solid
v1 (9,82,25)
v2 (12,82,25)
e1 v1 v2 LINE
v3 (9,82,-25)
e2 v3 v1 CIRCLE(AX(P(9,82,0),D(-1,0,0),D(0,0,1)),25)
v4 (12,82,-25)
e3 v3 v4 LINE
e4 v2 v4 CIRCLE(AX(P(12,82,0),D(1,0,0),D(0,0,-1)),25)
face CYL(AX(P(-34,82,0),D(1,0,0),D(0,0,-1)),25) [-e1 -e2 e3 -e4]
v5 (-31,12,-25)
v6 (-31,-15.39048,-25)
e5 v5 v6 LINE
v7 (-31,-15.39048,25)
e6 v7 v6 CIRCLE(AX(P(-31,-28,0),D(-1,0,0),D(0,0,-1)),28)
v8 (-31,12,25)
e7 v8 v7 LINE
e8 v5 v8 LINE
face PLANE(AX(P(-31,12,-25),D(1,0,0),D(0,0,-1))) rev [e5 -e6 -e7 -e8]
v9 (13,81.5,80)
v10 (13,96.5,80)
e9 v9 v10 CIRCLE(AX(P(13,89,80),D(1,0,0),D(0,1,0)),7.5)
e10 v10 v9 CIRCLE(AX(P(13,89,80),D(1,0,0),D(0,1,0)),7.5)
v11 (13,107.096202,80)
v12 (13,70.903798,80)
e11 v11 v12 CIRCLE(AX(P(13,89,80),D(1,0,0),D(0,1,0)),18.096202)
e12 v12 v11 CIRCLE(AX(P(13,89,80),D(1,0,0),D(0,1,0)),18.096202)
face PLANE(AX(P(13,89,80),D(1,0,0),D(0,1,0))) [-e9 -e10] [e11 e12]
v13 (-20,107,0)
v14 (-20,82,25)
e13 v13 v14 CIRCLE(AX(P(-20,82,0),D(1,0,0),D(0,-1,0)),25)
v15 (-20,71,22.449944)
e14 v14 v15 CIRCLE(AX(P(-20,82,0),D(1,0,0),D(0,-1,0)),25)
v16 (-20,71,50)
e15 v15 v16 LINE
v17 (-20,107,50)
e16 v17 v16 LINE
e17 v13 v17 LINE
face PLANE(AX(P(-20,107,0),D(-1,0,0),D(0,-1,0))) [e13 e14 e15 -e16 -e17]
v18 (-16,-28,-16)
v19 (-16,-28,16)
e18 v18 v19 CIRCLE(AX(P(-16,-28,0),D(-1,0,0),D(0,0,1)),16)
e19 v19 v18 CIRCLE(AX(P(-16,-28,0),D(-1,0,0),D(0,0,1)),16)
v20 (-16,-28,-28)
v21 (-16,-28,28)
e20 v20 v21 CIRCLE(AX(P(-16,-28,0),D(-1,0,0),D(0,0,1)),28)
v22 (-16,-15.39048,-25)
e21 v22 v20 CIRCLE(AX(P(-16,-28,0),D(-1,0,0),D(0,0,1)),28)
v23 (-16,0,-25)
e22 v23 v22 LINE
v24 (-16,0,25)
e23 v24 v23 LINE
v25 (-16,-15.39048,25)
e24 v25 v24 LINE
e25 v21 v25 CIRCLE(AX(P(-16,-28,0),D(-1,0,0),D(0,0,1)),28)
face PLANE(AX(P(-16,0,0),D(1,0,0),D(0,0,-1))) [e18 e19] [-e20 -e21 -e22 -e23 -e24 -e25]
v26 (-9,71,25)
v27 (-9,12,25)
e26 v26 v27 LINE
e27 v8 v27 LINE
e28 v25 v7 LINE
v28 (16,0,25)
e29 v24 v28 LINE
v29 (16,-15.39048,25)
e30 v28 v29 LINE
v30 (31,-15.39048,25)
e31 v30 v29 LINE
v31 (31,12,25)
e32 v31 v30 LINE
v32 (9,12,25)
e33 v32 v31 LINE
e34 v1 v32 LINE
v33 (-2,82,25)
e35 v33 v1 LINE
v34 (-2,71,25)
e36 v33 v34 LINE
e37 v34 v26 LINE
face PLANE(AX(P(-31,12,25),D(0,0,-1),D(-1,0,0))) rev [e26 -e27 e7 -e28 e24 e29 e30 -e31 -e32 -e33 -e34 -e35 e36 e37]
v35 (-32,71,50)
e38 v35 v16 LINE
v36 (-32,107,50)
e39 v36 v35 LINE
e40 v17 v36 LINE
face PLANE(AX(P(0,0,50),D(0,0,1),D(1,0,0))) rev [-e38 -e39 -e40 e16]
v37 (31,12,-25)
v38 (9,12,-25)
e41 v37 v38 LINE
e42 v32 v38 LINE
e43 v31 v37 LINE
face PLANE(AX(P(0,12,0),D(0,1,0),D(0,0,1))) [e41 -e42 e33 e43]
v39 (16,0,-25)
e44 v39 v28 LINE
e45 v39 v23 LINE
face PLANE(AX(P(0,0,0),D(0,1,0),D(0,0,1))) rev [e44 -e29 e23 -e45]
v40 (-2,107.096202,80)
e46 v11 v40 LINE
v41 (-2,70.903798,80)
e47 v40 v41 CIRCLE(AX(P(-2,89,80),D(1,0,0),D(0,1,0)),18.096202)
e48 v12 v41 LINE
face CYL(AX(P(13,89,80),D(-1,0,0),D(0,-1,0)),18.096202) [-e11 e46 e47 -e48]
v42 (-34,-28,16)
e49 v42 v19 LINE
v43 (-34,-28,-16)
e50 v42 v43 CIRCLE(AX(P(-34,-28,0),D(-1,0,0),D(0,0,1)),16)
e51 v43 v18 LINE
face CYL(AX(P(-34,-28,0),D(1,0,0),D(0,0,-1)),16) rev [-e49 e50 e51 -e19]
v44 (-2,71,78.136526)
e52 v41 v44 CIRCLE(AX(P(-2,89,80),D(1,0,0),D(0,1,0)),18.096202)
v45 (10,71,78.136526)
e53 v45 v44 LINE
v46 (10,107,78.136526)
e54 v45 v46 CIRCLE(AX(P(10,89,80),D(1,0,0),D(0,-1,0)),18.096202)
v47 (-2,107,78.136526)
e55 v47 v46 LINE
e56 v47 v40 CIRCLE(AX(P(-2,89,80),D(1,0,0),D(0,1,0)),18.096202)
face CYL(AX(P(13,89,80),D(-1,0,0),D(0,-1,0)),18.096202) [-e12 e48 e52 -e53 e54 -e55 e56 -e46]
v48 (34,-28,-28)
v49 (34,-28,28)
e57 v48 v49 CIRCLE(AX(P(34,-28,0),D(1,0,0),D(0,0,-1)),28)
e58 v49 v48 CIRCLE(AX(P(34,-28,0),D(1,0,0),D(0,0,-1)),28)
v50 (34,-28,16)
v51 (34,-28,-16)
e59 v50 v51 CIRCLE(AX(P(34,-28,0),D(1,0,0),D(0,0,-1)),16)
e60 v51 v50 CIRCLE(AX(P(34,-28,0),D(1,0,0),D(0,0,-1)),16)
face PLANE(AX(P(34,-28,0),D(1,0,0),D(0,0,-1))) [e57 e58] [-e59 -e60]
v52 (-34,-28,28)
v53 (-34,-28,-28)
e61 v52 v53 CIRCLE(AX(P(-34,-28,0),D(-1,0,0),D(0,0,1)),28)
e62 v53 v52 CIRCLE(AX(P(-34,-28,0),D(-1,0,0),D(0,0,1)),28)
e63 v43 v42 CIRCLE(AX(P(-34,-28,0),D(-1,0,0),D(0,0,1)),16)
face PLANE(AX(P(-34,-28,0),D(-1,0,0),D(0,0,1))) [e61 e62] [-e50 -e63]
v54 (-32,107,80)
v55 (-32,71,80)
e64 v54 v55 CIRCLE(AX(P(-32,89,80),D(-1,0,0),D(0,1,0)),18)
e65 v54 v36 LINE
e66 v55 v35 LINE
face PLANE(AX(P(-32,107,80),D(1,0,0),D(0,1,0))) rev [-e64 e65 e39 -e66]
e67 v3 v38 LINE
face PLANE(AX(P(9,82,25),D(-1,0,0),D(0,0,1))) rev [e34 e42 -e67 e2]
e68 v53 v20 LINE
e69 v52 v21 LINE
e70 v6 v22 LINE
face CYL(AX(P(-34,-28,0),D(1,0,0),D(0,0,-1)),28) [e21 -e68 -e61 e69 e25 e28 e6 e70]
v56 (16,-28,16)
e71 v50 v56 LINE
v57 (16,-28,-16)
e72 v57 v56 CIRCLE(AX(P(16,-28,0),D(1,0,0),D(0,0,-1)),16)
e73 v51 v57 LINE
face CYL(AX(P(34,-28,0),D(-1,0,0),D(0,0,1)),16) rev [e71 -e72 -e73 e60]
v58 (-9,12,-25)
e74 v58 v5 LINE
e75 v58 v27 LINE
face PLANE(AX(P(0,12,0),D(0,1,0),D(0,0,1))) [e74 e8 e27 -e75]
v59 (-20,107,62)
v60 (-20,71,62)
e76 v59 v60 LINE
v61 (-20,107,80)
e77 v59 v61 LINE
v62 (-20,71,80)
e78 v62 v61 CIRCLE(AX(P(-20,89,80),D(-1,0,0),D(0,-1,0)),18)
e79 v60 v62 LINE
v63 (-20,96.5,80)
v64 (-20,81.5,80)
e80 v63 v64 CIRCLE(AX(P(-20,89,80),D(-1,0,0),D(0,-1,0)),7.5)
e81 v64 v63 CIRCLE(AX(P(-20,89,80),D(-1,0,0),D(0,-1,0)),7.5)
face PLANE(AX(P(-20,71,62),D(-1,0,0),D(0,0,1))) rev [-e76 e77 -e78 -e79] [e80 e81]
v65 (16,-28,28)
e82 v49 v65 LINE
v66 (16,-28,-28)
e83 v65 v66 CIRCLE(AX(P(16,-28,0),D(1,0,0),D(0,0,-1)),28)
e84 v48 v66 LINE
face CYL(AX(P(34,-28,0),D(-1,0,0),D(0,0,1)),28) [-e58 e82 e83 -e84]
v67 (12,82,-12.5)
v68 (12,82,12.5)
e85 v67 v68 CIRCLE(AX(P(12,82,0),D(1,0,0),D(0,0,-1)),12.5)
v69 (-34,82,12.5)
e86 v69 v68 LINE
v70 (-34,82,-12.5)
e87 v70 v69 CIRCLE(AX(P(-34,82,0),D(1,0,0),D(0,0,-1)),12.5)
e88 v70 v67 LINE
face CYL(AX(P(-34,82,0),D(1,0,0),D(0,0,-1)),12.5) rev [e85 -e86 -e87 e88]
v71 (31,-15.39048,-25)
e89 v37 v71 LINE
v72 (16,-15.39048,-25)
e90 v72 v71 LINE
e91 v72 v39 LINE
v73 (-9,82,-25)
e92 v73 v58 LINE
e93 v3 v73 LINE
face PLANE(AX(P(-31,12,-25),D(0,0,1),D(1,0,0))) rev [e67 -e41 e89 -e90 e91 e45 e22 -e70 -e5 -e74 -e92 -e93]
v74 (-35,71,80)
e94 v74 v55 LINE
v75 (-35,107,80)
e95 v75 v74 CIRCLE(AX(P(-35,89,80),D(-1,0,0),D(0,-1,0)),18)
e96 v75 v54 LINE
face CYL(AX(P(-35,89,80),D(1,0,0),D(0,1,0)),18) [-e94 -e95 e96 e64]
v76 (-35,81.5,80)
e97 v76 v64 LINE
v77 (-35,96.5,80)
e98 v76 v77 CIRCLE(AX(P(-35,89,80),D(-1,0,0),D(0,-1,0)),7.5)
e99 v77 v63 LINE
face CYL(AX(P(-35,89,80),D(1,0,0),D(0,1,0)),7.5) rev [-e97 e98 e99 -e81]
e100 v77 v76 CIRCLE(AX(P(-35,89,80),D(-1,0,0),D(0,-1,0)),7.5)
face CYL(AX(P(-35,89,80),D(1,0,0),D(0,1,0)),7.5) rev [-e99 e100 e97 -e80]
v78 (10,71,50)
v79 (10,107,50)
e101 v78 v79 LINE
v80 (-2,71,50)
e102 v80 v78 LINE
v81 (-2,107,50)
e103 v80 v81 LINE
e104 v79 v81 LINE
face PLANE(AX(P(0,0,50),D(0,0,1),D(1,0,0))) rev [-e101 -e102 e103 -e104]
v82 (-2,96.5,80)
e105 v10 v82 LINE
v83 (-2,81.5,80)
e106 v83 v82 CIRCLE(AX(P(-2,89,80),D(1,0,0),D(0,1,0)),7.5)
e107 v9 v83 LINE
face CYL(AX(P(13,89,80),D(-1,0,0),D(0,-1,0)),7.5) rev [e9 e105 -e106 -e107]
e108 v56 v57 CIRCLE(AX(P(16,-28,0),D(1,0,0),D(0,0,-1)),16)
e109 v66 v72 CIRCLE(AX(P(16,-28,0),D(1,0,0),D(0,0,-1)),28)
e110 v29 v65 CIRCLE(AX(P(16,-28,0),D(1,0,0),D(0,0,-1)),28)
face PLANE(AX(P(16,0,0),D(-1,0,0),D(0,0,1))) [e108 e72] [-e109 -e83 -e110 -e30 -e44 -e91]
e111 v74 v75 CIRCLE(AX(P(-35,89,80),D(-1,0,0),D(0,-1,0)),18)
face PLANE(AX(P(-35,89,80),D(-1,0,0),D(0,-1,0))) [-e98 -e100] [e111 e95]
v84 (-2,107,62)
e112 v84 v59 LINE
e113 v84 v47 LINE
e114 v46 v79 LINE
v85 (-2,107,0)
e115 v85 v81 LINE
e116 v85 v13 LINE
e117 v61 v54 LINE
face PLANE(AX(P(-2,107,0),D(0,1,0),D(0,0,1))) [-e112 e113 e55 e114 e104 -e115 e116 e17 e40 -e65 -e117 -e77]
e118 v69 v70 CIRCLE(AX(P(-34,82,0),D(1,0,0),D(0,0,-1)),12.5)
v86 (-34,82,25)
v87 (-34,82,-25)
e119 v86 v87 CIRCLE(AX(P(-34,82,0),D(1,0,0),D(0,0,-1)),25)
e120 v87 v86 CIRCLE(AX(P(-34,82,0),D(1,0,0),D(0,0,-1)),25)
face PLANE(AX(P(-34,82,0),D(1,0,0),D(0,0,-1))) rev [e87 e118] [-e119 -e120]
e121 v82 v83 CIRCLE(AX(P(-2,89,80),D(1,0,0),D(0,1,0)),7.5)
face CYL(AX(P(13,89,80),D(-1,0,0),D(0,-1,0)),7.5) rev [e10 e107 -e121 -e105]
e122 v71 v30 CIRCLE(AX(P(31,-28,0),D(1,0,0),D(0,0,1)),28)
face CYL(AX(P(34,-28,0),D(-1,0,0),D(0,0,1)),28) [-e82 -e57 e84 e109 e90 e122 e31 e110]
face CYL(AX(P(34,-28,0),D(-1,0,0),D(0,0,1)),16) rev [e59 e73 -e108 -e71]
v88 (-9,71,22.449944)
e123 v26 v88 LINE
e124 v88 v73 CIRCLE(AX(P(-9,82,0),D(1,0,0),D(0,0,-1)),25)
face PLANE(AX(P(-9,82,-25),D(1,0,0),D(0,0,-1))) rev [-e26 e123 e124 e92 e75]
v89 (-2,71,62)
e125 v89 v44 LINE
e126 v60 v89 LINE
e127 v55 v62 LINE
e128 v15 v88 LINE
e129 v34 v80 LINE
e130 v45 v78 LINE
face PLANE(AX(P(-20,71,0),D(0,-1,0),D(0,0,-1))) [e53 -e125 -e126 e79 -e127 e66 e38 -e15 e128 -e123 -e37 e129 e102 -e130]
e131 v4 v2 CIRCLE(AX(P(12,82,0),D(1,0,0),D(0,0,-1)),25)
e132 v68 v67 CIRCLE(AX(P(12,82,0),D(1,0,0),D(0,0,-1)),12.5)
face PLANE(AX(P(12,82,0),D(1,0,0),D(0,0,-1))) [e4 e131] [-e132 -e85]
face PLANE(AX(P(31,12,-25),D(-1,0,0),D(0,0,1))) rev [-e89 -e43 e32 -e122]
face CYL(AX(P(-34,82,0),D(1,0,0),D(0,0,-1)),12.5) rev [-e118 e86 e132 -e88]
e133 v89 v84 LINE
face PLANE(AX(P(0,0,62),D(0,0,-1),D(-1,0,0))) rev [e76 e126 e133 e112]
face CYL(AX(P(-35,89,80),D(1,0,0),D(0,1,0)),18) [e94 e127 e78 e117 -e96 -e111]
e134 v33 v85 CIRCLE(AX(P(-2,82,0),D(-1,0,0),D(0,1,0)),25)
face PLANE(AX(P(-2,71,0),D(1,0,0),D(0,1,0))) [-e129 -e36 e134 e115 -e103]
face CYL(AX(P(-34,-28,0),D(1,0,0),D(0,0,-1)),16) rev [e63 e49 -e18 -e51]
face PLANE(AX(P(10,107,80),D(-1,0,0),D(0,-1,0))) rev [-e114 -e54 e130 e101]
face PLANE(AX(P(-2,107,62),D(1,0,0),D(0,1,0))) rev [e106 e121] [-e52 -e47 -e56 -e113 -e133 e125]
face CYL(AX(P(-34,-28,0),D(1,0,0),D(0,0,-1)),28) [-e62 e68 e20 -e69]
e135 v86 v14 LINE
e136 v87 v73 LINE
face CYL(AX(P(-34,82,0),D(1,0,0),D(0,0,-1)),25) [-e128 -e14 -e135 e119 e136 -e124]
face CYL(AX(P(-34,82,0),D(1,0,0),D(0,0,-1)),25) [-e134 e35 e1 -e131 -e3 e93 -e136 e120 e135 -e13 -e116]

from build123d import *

# Parameters (mm, degrees)
BASE_PLATE_SKETCH_W              = 62
BASE_PLATE_SKETCH_H              = 50
BASE_PLATE_62X50X12_DEPTH        = 12
COLUMN_SKETCH_W                  = 18
COLUMN_SKETCH_H                  = 50
COLUMN_9X9_DEPTH                 = 70
UPPER_HUB_DEPTH                  = 3
UPPER_HUB_DEPTH_BACK             = 43
UPPER_HUB_SKETCH_R               = 25
UPPER_HUB_SKETCH_R_2             = 12.5
LOWER_EAR_A_BLOCK_SKETCH_W       = 50
LOWER_EAR_A_BLOCK_SKETCH_H       = 28
LOWER_EAR_A_BLOCK_DEPTH          = 15
LOWER_EAR_A_ROUND_END_DEPTH      = 3
LOWER_EAR_A_ROUND_END_DEPTH_BACK = 15
LOWER_EAR_A_ROUND_END_SKETCH_R   = 28
LOWER_EAR_A_ROUND_END_SKETCH_R_2 = 16
LOWER_EAR_A_PIN_HOLE_SKETCH_R    = 16
LOWER_EAR_A_PIN_HOLE_DEPTH       = 15
LOWER_EAR_B_BLOCK_SKETCH_W       = 50
LOWER_EAR_B_BLOCK_SKETCH_H       = 28
LOWER_EAR_B_BLOCK_DEPTH          = 15
LOWER_EAR_B_ROUND_END_DEPTH      = 3
LOWER_EAR_B_ROUND_END_DEPTH_BACK = 15
LOWER_EAR_B_ROUND_END_SKETCH_R   = 28
LOWER_EAR_B_ROUND_END_SKETCH_R_2 = 16
LOWER_START                      = -15
LOWER_EAR_B_PIN_HOLE_SKETCH_R    = 16
LOWER_EAR_B_PIN_HOLE_DEPTH       = 15
UPPER_BRACKET_BLOCK_DEPTH        = 25
UPPER_BRACKET_BLOCK_DEPTH_BACK   = 25
UPPER_BRACKET_BLOCK_SKETCH_W     = 18
UPPER_BRACKET_BLOCK_SKETCH_H     = 36
UPPER_CLEVIS_ARM_SKETCH_W        = 42
UPPER_CLEVIS_ARM_SKETCH_H        = 36
UPPER_CLEVIS_ARM_DEPTH           = 30
CLEVIS_SLOT_SKETCH_W             = 18
CLEVIS_SLOT_SKETCH_H             = 36
CLEVIS_SLOT_12X12_DEPTH          = 18
UPPER_EAR_A_ROUND_END_DEPTH      = 3
UPPER_EAR_A_ROUND_END_DEPTH_BACK = 12
UPPER_EAR_A_ROUND_END_SKETCH_R   = 18.096202238
UPPER_EAR_A_ROUND_END_SKETCH_R_2 = 7.5
UPPER_EAR_A_PIN_HOLE_SKETCH_R    = 7.5
UPPER_EAR_A_PIN_HOLE_DEPTH       = 12
UPPER_EAR_B_ROUND_END_DEPTH      = 3
UPPER_EAR_B_ROUND_END_DEPTH_BACK = 12
UPPER_EAR_B_ROUND_END_SKETCH_R   = 18
UPPER_EAR_B_ROUND_END_SKETCH_R_2 = 7.5
UPPER_START                      = -12
UPPER_EAR_B_PIN_HOLE_SKETCH_R    = 7.5
UPPER_EAR_B_PIN_HOLE_DEPTH       = 12
HUB_BORE_SKETCH_R                = 12.5
HUB_BORE_THROUGH_DEPTH           = 66


with BuildPart() as part:
    # Base Plate Sketch → Base Plate 62x50x12 (new body)
    with BuildSketch(Plane(origin=(0, 0, 0), x_dir=(1, 0, 0), z_dir=(0, 1, 0))):
        Rectangle(BASE_PLATE_SKETCH_W, BASE_PLATE_SKETCH_H)
    extrude(amount=BASE_PLATE_62X50X12_DEPTH)

    # Column Sketch → Column 9x9 (add)
    with BuildSketch(Plane(origin=(0, 12, 0), x_dir=(1, 0, 0), z_dir=(0, 1, 0))):
        Rectangle(COLUMN_SKETCH_W, COLUMN_SKETCH_H)
    extrude(amount=COLUMN_9X9_DEPTH)

    # Upper Hub Sketch → Upper Hub (add, two sides: drawn at the far end of the back side and taken through both)
    with BuildSketch(Plane(origin=(9, 0, 0), x_dir=(0, 0, -1), z_dir=(1, 0, 0)).offset(-UPPER_HUB_DEPTH_BACK)):
        with Locations((0, 82)):
            Circle(UPPER_HUB_SKETCH_R)
        with Locations((0, 82)):
            Circle(UPPER_HUB_SKETCH_R_2, mode=Mode.SUBTRACT)
    extrude(amount=UPPER_HUB_DEPTH + UPPER_HUB_DEPTH_BACK)

    # Lower Ear A Block Sketch → Lower Ear A Block (add)
    with BuildSketch(Plane(origin=(31, 0, 0), x_dir=(0, 0, -1), z_dir=(1, 0, 0))):
        with Locations((0, -14)):
            Rectangle(LOWER_EAR_A_BLOCK_SKETCH_W, LOWER_EAR_A_BLOCK_SKETCH_H)
    extrude(amount=-LOWER_EAR_A_BLOCK_DEPTH)

    # Lower Ear A Round End Sketch → Lower Ear A Round End (add, two sides: drawn at the far end of the back side and taken through both)
    with BuildSketch(Plane(origin=(31, 0, 0), x_dir=(0, 0, -1), z_dir=(1, 0, 0)).offset(-LOWER_EAR_A_ROUND_END_DEPTH_BACK)):
        with Locations(Location((0, -28, 0), (0, 0, 153.234499423))):
            Circle(LOWER_EAR_A_ROUND_END_SKETCH_R)
        with Locations((0, -28)):
            Circle(LOWER_EAR_A_ROUND_END_SKETCH_R_2, mode=Mode.SUBTRACT)
    extrude(amount=LOWER_EAR_A_ROUND_END_DEPTH + LOWER_EAR_A_ROUND_END_DEPTH_BACK)

    # Lower Ear A Pin Hole Sketch → Lower Ear A Pin Hole (cut)
    with BuildSketch(Plane(origin=(31, 0, 0), x_dir=(0, 0, -1), z_dir=(1, 0, 0))):
        with Locations((0, -28)):
            Circle(LOWER_EAR_A_PIN_HOLE_SKETCH_R)
    extrude(amount=-LOWER_EAR_A_PIN_HOLE_DEPTH, mode=Mode.SUBTRACT)

    # Lower Ear B Block Sketch → Lower Ear B Block (add)
    with BuildSketch(Plane.ZY.offset(31)):
        with Locations((0, -14)):
            Rectangle(LOWER_EAR_B_BLOCK_SKETCH_W, LOWER_EAR_B_BLOCK_SKETCH_H)
    extrude(amount=-LOWER_EAR_B_BLOCK_DEPTH)

    # Lower Ear B Round End Sketch → Lower Ear B Round End (add, two sides: drawn at the far end of the back side and taken through both)
    with BuildSketch(Plane.ZY.offset(31).offset(-LOWER_EAR_B_ROUND_END_DEPTH_BACK)):
        with Locations(Location((0, -28, 0), (0, 0, 26.765500577))):
            Circle(LOWER_EAR_B_ROUND_END_SKETCH_R)
        with Locations(Location((0, -28, 0), (0, 0, 180))):
            Circle(LOWER_EAR_B_ROUND_END_SKETCH_R_2, mode=Mode.SUBTRACT)
    extrude(amount=LOWER_EAR_B_ROUND_END_DEPTH + LOWER_EAR_B_ROUND_END_DEPTH_BACK)

    # Lower Ear B Pin Hole Sketch → Lower Ear B Pin Hole (cut)
    with BuildSketch(Plane.ZY.offset(31).offset(LOWER_START)):
        with Locations(Location((0, -28, 0), (0, 0, 180))):
            Circle(LOWER_EAR_B_PIN_HOLE_SKETCH_R)
    extrude(amount=LOWER_EAR_B_PIN_HOLE_DEPTH, mode=Mode.SUBTRACT)

    # Upper Bracket Block Sketch → Upper Bracket Block (add, two sides: drawn at the far end of the back side and taken through both)
    with BuildSketch(Plane.XY.offset(25).offset(-UPPER_BRACKET_BLOCK_DEPTH_BACK)):
        with Locations((-11, 89)):
            Rectangle(UPPER_BRACKET_BLOCK_SKETCH_W, UPPER_BRACKET_BLOCK_SKETCH_H)
    extrude(amount=UPPER_BRACKET_BLOCK_DEPTH + UPPER_BRACKET_BLOCK_DEPTH_BACK)

    # Upper Clevis Arm Sketch → Upper Clevis Arm (add)
    with BuildSketch(Plane.XY.offset(50)):
        with Locations((-11, 89)):
            Rectangle(UPPER_CLEVIS_ARM_SKETCH_W, UPPER_CLEVIS_ARM_SKETCH_H)
    extrude(amount=UPPER_CLEVIS_ARM_DEPTH)

    # Clevis Slot Sketch → Clevis Slot 12x12 (cut)
    with BuildSketch(Plane.XY.offset(80)):
        with Locations((-11, 89)):
            Rectangle(CLEVIS_SLOT_SKETCH_W, CLEVIS_SLOT_SKETCH_H)
    extrude(amount=-CLEVIS_SLOT_12X12_DEPTH, mode=Mode.SUBTRACT)

    # Upper Ear A Round End Sketch → Upper Ear A Round End (add, two sides: drawn at the far end of the back side and taken through both)
    with BuildSketch(Plane(origin=(10, 0, 0), x_dir=(0, 0, -1), z_dir=(1, 0, 0)).offset(-UPPER_EAR_A_ROUND_END_DEPTH_BACK)):
        with Locations(Location((-80, 89, 0), (0, 0, 275.910566162))):
            Circle(UPPER_EAR_A_ROUND_END_SKETCH_R)
        with Locations(Location((-80, 89, 0), (0, 0, 90))):
            Circle(UPPER_EAR_A_ROUND_END_SKETCH_R_2, mode=Mode.SUBTRACT)
    extrude(amount=UPPER_EAR_A_ROUND_END_DEPTH + UPPER_EAR_A_ROUND_END_DEPTH_BACK)

    # Upper Ear A Pin Hole Sketch → Upper Ear A Pin Hole (cut)
    with BuildSketch(Plane(origin=(10, 0, 0), x_dir=(0, 0, -1), z_dir=(1, 0, 0))):
        with Locations(Location((-80, 89, 0), (0, 0, 90))):
            Circle(UPPER_EAR_A_PIN_HOLE_SKETCH_R)
    extrude(amount=-UPPER_EAR_A_PIN_HOLE_DEPTH, mode=Mode.SUBTRACT)

    # Upper Ear B Round End Sketch → Upper Ear B Round End (add, two sides: drawn at the far end of the back side and taken through both)
    with BuildSketch(Plane.ZY.offset(32).offset(-UPPER_EAR_B_ROUND_END_DEPTH_BACK)):
        with Locations(Location((80, 89, 0), (0, 0, 270))):
            Circle(UPPER_EAR_B_ROUND_END_SKETCH_R)
        with Locations(Location((80, 89, 0), (0, 0, 90))):
            Circle(UPPER_EAR_B_ROUND_END_SKETCH_R_2, mode=Mode.SUBTRACT)
    extrude(amount=UPPER_EAR_B_ROUND_END_DEPTH + UPPER_EAR_B_ROUND_END_DEPTH_BACK)

    # Upper Ear B Pin Hole Sketch → Upper Ear B Pin Hole (cut)
    with BuildSketch(Plane.ZY.offset(32).offset(UPPER_START)):
        with Locations(Location((80, 89, 0), (0, 0, 90))):
            Circle(UPPER_EAR_B_PIN_HOLE_SKETCH_R)
    extrude(amount=UPPER_EAR_B_PIN_HOLE_DEPTH, mode=Mode.SUBTRACT)

    # Hub Bore Sketch → Hub Bore Through (cut)
    with BuildSketch(Plane.ZY.offset(34)):
        with Locations(Location((0, 82, 0), (0, 0, 180))):
            Circle(HUB_BORE_SKETCH_R)
    extrude(amount=-HUB_BORE_THROUGH_DEPTH, mode=Mode.SUBTRACT)


solid = part.part
